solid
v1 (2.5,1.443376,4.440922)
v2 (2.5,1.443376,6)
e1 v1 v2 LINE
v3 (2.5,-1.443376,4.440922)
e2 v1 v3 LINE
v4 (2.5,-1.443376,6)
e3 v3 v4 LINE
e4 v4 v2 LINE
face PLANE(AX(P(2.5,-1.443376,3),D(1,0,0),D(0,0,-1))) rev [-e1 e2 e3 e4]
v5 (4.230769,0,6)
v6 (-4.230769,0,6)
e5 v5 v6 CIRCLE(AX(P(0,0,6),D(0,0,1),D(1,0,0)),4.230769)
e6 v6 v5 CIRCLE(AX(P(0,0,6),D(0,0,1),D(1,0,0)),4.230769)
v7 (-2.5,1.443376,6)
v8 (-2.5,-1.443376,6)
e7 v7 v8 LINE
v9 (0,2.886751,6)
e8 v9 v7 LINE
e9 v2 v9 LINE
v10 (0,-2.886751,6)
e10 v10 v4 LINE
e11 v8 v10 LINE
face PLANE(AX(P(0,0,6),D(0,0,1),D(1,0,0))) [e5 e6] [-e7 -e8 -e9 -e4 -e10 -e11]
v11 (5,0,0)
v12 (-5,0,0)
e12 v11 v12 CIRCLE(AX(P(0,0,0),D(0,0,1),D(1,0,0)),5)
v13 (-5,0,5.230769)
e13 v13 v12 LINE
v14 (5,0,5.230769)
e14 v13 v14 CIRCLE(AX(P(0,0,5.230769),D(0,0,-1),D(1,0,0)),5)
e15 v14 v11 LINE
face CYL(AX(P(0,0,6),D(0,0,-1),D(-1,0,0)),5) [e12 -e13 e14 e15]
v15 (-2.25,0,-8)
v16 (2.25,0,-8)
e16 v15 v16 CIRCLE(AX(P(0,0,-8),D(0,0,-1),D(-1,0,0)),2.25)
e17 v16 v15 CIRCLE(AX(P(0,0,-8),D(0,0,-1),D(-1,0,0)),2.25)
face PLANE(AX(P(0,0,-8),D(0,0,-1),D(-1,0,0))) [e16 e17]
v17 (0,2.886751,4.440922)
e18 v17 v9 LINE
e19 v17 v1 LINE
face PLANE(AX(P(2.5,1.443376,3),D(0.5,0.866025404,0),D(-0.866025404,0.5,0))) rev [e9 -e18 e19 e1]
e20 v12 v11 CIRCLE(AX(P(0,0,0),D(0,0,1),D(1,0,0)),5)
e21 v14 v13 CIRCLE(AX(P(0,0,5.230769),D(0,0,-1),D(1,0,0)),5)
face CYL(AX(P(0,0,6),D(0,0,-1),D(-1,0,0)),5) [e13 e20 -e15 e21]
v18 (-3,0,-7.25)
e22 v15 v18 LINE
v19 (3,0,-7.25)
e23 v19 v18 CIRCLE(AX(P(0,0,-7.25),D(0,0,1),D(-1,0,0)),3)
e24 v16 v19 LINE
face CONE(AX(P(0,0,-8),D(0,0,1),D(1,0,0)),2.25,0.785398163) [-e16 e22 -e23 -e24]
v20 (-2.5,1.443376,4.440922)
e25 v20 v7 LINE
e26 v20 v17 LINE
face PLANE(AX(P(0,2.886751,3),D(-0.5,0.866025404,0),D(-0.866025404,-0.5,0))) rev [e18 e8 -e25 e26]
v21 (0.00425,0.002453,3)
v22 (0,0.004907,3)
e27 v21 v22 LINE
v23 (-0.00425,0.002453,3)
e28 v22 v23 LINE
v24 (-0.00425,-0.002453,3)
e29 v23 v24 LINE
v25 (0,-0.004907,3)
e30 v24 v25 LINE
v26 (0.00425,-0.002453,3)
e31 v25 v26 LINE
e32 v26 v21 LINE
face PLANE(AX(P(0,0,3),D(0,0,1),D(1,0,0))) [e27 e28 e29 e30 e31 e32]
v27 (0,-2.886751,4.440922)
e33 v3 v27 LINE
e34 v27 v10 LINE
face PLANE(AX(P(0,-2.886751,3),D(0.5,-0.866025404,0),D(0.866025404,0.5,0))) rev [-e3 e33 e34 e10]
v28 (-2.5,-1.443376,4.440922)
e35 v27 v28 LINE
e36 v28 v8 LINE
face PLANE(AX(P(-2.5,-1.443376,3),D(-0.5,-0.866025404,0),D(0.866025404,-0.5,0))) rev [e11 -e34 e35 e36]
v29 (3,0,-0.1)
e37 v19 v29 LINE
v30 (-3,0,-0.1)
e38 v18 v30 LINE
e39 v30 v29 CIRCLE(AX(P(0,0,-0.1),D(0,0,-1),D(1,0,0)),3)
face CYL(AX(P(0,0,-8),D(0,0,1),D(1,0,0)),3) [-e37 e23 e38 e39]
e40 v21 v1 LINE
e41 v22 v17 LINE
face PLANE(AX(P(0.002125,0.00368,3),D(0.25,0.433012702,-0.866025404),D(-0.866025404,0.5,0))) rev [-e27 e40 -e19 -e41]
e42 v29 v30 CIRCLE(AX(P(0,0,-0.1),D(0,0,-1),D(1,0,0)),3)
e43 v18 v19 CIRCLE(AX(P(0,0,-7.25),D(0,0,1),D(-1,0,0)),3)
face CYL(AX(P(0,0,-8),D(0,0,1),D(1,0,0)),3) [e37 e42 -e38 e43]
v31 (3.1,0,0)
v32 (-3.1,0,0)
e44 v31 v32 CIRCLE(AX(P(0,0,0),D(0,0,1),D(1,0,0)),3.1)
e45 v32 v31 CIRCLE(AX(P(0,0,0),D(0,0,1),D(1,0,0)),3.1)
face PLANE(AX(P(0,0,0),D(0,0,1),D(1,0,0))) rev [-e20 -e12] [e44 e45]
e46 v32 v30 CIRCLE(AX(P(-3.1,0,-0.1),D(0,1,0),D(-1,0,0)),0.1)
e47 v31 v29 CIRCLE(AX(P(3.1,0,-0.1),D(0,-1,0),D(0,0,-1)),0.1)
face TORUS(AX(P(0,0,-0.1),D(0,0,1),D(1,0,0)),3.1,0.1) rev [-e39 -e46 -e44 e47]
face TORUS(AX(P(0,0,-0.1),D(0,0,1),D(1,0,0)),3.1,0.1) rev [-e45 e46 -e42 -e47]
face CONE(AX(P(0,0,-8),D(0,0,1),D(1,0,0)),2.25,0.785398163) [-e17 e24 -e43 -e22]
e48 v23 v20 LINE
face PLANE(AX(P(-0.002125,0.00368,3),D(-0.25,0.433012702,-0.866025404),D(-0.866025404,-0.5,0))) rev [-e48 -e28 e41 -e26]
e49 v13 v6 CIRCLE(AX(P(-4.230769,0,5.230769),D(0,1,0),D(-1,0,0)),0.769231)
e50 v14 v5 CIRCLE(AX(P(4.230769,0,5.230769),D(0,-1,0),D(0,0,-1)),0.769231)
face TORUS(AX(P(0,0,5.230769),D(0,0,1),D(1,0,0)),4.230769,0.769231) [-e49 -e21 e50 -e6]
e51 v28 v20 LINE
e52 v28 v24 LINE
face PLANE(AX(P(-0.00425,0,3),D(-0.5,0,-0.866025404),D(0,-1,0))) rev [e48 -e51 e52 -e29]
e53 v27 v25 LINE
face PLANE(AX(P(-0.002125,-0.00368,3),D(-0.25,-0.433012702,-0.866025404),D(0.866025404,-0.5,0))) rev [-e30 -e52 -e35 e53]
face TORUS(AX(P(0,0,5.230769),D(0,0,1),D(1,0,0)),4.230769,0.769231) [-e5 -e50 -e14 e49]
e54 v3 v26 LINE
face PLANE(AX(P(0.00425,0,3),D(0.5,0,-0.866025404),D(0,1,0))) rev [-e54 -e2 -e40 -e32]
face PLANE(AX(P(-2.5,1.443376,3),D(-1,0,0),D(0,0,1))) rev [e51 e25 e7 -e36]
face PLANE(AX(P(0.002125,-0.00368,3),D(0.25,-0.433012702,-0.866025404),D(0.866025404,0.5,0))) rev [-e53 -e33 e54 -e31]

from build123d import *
from OCP.BRepFilletAPI import BRepFilletAPI_MakeChamfer

# Parameters (mm, degrees)
SKETCH_1_R          = 5
EXTRUDE_1_DEPTH     = 6
CUT_EXTRUDE_1_DEPTH = 3
SKETCH_3_R          = 3
EXTRUDE_2_DEPTH     = 8
CHAMFER_1_SIZE      = 0.75
FILLET_1_R          = 0.769230769
CHAMFER_2_SIZE      = 1.44092219
CHAMFER_2_SIZE2     = 2.495750443
FILLET_2_R          = 0.1


with BuildPart() as part:
    # 草图1 → 凸台-拉伸1 (new body)
    with BuildSketch(Plane.XY):
        Circle(SKETCH_1_R)
    extrude(amount=EXTRUDE_1_DEPTH)

    # 草图2 → 切除-拉伸1 (cut)
    with BuildSketch(Plane.XY.offset(6)):
        Polygon((2.5, 1.443375673), (0, 2.886751346), (-2.5, 1.443375673), (-2.5, -1.443375673), (0, -2.886751346), (2.5, -1.443375673), align=None)
    extrude(amount=-CUT_EXTRUDE_1_DEPTH, mode=Mode.SUBTRACT)

    # 草图3 → 凸台-拉伸2 (add)
    with BuildSketch(Plane(origin=(0, 0, 0), x_dir=(-1, 0, 0), z_dir=(0, 0, -1))):
        with Locations(Location((0, 0, 0), (0, 0, 180))):
            Circle(SKETCH_3_R)
    extrude(amount=EXTRUDE_2_DEPTH)

    # 倒角1
    chamfer_1_edges = [part.edges().sort_by_distance(p)[0] for p in [
        (-3, 0, -8),
    ]]
    chamfer(chamfer_1_edges, length=CHAMFER_1_SIZE)

    # 圆角1
    fillet_1_edges = [part.edges().sort_by_distance(p)[0] for p in [
        (-5, 0, 6),
    ]]
    fillet(fillet_1_edges, radius=FILLET_1_R)

    # 倒角2: one chamfer whose edges measure the first distance from different faces: ONE call of the kernel's chamfer builder (chamfer() names one face for all edges)
    chamfer_2_edges_1 = [part.edges().sort_by_distance(p)[0] for p in [
        (1.25, 2.165063509, 3),
    ]]
    chamfer_2_side_1 = [part.faces().sort_by_distance(p)[0] for p in [
        (1.25, 2.165063509, 4.5),
    ]]
    chamfer_2_edges_2 = [part.edges().sort_by_distance(p)[0] for p in [
        (2.5, 0, 3),
    ]]
    chamfer_2_side_2 = [part.faces().sort_by_distance(p)[0] for p in [
        (2.5, 0, 4.5),
    ]]
    chamfer_2_edges_3 = [part.edges().sort_by_distance(p)[0] for p in [
        (1.25, -2.165063509, 3),
    ]]
    chamfer_2_side_3 = [part.faces().sort_by_distance(p)[0] for p in [
        (1.25, -2.165063509, 4.5),
    ]]
    chamfer_2_edges_4 = [part.edges().sort_by_distance(p)[0] for p in [
        (-1.25, -2.165063509, 3),
    ]]
    chamfer_2_side_4 = [part.faces().sort_by_distance(p)[0] for p in [
        (-1.25, -2.165063509, 4.5),
    ]]
    chamfer_2_edges_5 = [part.edges().sort_by_distance(p)[0] for p in [
        (-2.5, 0, 3),
    ]]
    chamfer_2_side_5 = [part.faces().sort_by_distance(p)[0] for p in [
        (-2.5, 0, 4.5),
    ]]
    chamfer_2_edges_6 = [part.edges().sort_by_distance(p)[0] for p in [
        (-1.25, 2.165063509, 3),
    ]]
    chamfer_2_side_6 = [part.faces().sort_by_distance(p)[0] for p in [
        (-1.25, 2.165063509, 4.5),
    ]]
    chamfer_2 = BRepFilletAPI_MakeChamfer(part.part.solid().wrapped)
    for e in chamfer_2_edges_1:
        chamfer_2.Add(CHAMFER_2_SIZE, CHAMFER_2_SIZE2, e.wrapped, chamfer_2_side_1[0].wrapped)  # the first distance lies on this face
    for e in chamfer_2_edges_2:
        chamfer_2.Add(CHAMFER_2_SIZE, CHAMFER_2_SIZE2, e.wrapped, chamfer_2_side_2[0].wrapped)  # the first distance lies on this face
    for e in chamfer_2_edges_3:
        chamfer_2.Add(CHAMFER_2_SIZE, CHAMFER_2_SIZE2, e.wrapped, chamfer_2_side_3[0].wrapped)  # the first distance lies on this face
    for e in chamfer_2_edges_4:
        chamfer_2.Add(CHAMFER_2_SIZE, CHAMFER_2_SIZE2, e.wrapped, chamfer_2_side_4[0].wrapped)  # the first distance lies on this face
    for e in chamfer_2_edges_5:
        chamfer_2.Add(CHAMFER_2_SIZE, CHAMFER_2_SIZE2, e.wrapped, chamfer_2_side_5[0].wrapped)  # the first distance lies on this face
    for e in chamfer_2_edges_6:
        chamfer_2.Add(CHAMFER_2_SIZE, CHAMFER_2_SIZE2, e.wrapped, chamfer_2_side_6[0].wrapped)  # the first distance lies on this face
    add(Compound.cast(chamfer_2.Shape()), mode=Mode.REPLACE)

    # 圆角2
    fillet_2_edges = [part.edges().sort_by_distance(p)[0] for p in [
        (-3, 0, 0),
    ]]
    fillet(fillet_2_edges, radius=FILLET_2_R)


solid = part.part
